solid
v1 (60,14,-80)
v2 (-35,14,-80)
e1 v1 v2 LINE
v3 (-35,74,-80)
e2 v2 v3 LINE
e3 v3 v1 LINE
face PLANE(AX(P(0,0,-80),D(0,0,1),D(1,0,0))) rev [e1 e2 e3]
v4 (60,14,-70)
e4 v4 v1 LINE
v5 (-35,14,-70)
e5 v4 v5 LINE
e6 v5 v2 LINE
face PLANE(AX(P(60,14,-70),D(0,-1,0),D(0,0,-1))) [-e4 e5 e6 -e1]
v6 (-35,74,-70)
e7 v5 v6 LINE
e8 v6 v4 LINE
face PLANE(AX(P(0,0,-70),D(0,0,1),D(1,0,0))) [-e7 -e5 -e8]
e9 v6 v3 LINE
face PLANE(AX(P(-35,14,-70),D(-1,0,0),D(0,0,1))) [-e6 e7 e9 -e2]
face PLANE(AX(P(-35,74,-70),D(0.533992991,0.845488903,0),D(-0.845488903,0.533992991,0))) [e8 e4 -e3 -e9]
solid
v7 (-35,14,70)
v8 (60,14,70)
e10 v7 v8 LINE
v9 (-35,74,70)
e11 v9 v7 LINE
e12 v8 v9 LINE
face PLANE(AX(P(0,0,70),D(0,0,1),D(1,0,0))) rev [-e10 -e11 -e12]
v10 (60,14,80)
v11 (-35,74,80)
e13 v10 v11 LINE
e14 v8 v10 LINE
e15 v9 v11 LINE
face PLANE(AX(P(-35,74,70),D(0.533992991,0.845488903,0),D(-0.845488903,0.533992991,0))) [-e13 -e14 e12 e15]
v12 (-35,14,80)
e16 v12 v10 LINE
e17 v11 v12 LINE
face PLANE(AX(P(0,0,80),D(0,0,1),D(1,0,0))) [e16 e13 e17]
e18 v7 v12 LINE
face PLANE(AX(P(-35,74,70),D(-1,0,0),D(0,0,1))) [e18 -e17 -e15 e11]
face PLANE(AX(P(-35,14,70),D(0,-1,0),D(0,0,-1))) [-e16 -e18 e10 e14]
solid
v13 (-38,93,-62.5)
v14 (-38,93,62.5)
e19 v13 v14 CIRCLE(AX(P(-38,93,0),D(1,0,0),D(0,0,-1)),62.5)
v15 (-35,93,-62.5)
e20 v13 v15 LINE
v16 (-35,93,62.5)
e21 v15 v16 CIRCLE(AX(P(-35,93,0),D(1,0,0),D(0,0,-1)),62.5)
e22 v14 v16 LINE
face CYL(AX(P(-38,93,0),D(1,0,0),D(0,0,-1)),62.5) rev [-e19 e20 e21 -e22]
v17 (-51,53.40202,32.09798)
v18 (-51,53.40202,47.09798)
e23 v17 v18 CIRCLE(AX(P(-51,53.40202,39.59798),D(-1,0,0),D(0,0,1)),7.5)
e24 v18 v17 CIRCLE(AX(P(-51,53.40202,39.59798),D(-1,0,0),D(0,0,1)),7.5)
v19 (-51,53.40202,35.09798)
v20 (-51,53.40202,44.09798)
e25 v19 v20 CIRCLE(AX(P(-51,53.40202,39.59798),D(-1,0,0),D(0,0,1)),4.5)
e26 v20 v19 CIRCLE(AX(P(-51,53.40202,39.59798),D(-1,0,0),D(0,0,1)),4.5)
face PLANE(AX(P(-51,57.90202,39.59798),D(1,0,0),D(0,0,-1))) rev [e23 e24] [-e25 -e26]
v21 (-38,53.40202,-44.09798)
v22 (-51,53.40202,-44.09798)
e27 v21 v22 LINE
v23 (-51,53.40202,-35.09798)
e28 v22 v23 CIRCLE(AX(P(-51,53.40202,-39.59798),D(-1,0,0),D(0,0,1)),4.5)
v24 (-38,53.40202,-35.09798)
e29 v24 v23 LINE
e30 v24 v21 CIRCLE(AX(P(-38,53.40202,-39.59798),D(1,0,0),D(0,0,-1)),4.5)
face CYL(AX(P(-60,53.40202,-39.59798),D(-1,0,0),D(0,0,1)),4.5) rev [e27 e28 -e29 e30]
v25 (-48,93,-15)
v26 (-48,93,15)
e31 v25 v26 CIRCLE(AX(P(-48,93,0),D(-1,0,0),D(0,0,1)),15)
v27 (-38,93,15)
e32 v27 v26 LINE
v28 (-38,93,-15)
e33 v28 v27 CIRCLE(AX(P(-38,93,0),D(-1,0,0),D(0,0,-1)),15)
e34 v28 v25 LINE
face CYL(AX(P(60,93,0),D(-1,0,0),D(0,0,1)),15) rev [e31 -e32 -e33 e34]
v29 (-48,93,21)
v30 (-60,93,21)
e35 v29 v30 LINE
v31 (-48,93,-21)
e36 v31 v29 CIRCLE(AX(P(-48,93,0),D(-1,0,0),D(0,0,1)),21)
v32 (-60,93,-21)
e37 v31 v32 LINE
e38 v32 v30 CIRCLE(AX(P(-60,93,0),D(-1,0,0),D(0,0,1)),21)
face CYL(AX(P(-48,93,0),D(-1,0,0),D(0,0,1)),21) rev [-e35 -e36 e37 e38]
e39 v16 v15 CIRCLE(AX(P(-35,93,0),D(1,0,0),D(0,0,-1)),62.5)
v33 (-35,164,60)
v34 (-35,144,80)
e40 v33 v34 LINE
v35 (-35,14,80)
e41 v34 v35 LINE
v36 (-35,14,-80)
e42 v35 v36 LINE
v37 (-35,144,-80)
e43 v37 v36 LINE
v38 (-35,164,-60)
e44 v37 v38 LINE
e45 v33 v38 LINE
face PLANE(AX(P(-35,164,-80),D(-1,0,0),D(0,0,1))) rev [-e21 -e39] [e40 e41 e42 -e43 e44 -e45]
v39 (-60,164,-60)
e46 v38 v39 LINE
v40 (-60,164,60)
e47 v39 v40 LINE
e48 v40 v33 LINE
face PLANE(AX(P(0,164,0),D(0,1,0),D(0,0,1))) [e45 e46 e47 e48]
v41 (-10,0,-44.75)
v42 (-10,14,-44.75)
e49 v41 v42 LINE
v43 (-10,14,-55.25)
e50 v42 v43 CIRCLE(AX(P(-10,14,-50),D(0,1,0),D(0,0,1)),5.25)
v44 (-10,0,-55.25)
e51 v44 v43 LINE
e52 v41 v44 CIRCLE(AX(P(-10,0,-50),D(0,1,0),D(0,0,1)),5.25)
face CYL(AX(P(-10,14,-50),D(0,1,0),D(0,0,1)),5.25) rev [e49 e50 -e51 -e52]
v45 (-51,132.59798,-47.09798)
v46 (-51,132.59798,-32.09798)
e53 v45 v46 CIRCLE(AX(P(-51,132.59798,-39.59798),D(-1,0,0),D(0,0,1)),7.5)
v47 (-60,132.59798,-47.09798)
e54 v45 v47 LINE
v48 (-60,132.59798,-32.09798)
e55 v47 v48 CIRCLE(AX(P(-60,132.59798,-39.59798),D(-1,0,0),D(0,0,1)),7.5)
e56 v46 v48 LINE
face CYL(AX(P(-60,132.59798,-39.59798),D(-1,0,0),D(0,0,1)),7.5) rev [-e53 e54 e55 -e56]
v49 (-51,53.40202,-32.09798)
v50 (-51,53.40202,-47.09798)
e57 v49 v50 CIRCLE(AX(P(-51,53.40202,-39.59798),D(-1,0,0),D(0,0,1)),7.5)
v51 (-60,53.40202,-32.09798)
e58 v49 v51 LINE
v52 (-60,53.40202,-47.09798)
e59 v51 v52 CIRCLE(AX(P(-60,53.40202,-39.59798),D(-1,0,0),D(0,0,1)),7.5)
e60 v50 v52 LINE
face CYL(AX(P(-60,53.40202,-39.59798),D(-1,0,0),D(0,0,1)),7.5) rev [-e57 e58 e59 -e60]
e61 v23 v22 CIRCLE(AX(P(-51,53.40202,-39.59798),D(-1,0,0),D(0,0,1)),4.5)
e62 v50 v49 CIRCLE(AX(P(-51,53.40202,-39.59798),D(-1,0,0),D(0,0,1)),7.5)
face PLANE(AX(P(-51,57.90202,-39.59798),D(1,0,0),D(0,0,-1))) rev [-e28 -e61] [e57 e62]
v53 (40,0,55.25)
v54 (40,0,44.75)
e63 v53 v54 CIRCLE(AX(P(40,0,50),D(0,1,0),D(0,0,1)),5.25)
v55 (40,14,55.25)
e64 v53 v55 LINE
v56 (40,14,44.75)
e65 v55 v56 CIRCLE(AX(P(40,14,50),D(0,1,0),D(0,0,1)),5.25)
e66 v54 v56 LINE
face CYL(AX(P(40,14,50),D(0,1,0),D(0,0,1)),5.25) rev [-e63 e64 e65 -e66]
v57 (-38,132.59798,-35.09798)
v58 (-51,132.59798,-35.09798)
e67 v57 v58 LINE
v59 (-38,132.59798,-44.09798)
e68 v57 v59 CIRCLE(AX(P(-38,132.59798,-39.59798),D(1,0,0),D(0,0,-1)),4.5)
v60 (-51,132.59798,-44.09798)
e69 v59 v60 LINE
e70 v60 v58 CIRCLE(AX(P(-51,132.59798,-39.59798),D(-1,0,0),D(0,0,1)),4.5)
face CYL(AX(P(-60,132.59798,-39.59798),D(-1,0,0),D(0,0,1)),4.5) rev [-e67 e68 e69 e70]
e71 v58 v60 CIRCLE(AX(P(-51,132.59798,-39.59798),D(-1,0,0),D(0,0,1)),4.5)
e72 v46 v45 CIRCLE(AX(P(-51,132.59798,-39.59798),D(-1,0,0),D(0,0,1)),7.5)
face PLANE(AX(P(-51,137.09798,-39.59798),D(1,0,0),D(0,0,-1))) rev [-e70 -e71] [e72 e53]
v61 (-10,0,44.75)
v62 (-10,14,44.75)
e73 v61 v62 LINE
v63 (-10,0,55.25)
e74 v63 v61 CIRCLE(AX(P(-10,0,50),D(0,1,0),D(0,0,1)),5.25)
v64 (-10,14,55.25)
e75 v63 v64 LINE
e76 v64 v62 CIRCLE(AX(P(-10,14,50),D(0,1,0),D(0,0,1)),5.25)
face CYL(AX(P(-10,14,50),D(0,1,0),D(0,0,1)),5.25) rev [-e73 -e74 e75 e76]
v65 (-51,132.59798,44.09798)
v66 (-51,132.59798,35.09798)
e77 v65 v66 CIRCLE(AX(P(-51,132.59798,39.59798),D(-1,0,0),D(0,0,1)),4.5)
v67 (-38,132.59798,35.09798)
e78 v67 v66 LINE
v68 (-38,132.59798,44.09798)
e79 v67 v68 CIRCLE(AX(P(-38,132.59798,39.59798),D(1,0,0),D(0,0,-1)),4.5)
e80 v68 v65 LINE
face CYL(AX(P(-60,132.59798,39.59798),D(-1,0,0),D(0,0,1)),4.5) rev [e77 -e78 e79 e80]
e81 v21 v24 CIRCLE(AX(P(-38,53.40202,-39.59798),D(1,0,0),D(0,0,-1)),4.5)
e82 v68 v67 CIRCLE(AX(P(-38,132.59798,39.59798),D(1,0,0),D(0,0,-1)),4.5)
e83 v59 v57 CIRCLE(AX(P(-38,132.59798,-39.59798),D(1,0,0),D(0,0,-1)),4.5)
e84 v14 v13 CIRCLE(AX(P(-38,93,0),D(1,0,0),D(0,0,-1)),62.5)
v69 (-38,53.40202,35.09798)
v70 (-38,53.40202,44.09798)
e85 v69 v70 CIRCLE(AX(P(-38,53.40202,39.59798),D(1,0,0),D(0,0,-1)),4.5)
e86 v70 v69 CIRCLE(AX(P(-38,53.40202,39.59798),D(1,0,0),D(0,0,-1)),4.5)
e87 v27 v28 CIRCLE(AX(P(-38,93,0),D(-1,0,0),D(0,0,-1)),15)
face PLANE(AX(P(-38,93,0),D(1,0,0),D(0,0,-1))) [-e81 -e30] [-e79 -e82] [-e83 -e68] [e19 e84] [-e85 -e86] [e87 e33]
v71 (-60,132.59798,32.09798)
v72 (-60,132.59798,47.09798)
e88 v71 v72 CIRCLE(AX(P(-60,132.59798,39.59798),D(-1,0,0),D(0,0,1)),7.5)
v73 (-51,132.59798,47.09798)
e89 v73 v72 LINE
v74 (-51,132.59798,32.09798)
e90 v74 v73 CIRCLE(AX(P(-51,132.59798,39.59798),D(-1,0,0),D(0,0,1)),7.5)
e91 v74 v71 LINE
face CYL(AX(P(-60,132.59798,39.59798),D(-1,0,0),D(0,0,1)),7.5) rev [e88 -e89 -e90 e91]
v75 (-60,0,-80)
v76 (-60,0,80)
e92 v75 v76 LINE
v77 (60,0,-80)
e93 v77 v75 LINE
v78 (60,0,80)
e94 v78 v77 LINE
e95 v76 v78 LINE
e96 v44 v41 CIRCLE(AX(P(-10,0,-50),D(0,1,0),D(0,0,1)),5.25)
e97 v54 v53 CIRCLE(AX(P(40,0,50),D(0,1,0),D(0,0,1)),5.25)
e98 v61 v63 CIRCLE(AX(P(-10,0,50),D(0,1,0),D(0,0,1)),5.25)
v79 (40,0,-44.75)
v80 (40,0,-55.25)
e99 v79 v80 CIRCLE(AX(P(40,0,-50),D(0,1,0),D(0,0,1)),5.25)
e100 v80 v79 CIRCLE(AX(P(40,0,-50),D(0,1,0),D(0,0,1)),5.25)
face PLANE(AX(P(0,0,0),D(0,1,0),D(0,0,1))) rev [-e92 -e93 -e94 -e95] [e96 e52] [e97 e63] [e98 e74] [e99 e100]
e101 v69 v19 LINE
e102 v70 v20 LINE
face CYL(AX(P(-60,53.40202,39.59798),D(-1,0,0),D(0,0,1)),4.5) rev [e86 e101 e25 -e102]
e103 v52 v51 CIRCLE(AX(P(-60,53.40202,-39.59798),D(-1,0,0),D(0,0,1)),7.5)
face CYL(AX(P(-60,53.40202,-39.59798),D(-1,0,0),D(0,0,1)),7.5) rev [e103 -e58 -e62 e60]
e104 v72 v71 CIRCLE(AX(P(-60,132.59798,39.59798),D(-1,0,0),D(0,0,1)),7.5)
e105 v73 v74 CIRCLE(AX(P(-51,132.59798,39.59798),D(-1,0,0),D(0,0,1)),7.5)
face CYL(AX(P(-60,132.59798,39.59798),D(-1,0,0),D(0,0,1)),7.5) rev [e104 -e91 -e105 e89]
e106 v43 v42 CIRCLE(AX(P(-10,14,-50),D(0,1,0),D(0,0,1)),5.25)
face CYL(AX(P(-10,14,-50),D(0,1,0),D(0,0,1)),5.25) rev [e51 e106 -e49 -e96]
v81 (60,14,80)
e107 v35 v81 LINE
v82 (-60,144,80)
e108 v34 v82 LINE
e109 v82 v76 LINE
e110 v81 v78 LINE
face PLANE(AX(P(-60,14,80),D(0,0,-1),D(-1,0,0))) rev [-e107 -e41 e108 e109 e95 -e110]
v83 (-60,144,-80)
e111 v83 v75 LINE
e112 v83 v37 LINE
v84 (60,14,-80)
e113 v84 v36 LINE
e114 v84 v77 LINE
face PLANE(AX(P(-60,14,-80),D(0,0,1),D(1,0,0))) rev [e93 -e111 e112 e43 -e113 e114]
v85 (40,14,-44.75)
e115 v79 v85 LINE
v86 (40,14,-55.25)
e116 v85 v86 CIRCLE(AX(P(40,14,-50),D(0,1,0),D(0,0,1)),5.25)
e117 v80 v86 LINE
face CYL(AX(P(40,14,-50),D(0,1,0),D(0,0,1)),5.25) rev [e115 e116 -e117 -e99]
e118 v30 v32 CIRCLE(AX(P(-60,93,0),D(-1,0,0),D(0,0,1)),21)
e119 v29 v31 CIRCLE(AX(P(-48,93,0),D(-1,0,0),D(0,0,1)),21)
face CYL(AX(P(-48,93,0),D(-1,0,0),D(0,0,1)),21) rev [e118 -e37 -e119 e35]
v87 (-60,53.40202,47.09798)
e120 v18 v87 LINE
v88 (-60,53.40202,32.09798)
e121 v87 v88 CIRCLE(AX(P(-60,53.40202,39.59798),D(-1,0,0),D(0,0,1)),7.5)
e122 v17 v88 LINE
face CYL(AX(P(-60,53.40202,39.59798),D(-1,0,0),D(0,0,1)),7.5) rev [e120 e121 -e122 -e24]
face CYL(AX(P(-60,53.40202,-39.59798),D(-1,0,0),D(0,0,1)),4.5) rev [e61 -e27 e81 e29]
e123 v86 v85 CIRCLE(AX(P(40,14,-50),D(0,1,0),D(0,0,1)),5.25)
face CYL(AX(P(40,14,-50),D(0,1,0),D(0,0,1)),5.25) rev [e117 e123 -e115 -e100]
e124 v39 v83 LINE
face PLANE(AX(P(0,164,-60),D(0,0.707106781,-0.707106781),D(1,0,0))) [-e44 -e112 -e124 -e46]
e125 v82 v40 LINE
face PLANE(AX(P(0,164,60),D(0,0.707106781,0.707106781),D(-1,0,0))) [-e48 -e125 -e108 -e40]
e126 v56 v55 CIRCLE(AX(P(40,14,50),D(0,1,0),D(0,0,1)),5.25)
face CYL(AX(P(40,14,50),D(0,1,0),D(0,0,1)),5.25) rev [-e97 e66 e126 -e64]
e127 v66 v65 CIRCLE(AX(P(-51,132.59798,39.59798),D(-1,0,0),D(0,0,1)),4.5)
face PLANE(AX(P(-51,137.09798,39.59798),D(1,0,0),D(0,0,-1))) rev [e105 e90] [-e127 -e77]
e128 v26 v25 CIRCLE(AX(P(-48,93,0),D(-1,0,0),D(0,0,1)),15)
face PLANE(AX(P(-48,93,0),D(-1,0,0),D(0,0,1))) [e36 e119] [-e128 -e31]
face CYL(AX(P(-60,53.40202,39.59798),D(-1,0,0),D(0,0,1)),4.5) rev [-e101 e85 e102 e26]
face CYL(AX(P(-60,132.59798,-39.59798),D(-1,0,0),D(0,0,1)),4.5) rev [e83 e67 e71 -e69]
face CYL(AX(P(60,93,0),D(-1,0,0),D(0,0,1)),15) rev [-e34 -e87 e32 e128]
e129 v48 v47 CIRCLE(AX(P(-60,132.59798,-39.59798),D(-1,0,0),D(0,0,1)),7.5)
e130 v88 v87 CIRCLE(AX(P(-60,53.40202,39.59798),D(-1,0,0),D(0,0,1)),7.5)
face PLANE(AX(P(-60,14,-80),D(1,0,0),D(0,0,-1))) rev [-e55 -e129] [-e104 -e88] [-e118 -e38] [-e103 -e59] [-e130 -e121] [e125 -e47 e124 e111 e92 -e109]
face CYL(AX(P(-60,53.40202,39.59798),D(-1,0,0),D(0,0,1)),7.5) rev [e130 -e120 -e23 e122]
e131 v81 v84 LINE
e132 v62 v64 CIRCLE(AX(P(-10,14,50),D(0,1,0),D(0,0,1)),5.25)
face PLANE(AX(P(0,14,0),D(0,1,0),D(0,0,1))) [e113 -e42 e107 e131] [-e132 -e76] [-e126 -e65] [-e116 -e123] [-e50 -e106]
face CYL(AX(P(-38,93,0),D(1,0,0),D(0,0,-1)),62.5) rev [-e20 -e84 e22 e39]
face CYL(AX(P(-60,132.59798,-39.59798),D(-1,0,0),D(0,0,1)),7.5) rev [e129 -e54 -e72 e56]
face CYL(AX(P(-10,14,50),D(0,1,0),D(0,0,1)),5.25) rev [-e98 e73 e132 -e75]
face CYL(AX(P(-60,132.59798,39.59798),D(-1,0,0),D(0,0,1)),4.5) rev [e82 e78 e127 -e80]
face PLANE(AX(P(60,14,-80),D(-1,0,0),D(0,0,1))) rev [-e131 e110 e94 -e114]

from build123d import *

# Parameters (mm, degrees)
SKETCH_1_W                         = 120
SKETCH_1_H                         = 160
EXTRUDE_1_DEPTH                    = 14
SKETCH_2_W                         = 25
SKETCH_2_H                         = 160
EXTRUDE_2_DEPTH                    = 150
EXTRUDE_3_DEPTH                    = 10
EXTRUDE_4_DEPTH                    = 10
SKETCH_5_R                         = 21
CUT_EXTRUDE_1_DEPTH                = 12
SKETCH_6_R                         = 15
CUT_EXTRUDE_2_DEPTH                = 213.037732491
SKETCH_7_R                         = 62.5
CUT_EXTRUDE_3_DEPTH                = 3
HOLE_WIZARD_10_5_10_5_1_AT_2_COUNT = 2
HOLE_WIZARD_10_5_10_5_1_AT_2_PITCH = 100
PATTERN_LINEAR_1_COUNT             = 2
PATTERN_LINEAR_1_PITCH             = 50
CHAMFER_1_SIZE                     = 20
PATTERN_CIRCULAR_1_COUNT           = 4


with BuildPart() as part:
    # 草图1 → 凸台-拉伸1 (new body)
    with BuildSketch(Plane(origin=(0, 0, 0), x_dir=(1, 0, 0), z_dir=(0, 1, 0))):
        Rectangle(SKETCH_1_W, SKETCH_1_H)
    extrude(amount=EXTRUDE_1_DEPTH)

    # 草图2 → 凸台-拉伸2 (add)
    with BuildSketch(Plane(origin=(0, 14, 0), x_dir=(1, 0, 0), z_dir=(0, 1, 0))):
        with Locations((-47.5, 0)):
            Rectangle(SKETCH_2_W, SKETCH_2_H)
    extrude(amount=EXTRUDE_2_DEPTH)

    # 草图5 → 切除-拉伸1 (cut)
    with BuildSketch(Plane.ZY.offset(60)):
        with Locations((0, 93)):
            Circle(SKETCH_5_R)
    extrude(amount=-CUT_EXTRUDE_1_DEPTH, mode=Mode.SUBTRACT)

    # 草图6 → 切除-拉伸2 (cut, through all)
    with BuildSketch(Plane.ZY.offset(48)):
        with Locations((0, 93)):
            Circle(SKETCH_6_R)
    extrude(amount=-CUT_EXTRUDE_2_DEPTH, mode=Mode.SUBTRACT)

    # 草图7 → 切除-拉伸3 (cut)
    with BuildSketch(Plane(origin=(-35, 0, 0), x_dir=(0, 0, -1), z_dir=(1, 0, 0))):
        with Locations((0, 93)):
            Circle(SKETCH_7_R)
    extrude(amount=-CUT_EXTRUDE_3_DEPTH, mode=Mode.SUBTRACT)

    # 草图9 → Ø10.5 (10.5) 直径孔1 (revolve, cut)
    with BuildSketch(Plane(origin=(40, 14, -50), x_dir=(0, 0, 1), z_dir=(1, 0, 0))):
        Polygon((0, 0), (0, 18.15451825), (5.25, 15), (5.25, 0), align=None)
    hole_wizard_10_5_10_5_1 = revolve(axis=Axis((40, 20.35, -50), (0, -1, 0)), mode=Mode.SUBTRACT)

    # Ø10.5 (10.5) 直径孔1 at 2: Ø10.5 (10.5) 直径孔1 ×2
    with Locations(*[(0, 0, i * HOLE_WIZARD_10_5_10_5_1_AT_2_PITCH) for i in range(1, HOLE_WIZARD_10_5_10_5_1_AT_2_COUNT)]):
        add(hole_wizard_10_5_10_5_1, mode=Mode.SUBTRACT)

    # 阵列(线性)1: Ø10.5 (10.5) 直径孔1 ×2
    with Locations(*[(-i * PATTERN_LINEAR_1_PITCH, 0, 0) for i in range(1, PATTERN_LINEAR_1_COUNT)]):
        add(hole_wizard_10_5_10_5_1, mode=Mode.SUBTRACT)

    # 阵列(线性)1 copy 1 sketch → 阵列(线性)1 copy 1 (revolve, cut)
    with BuildSketch(Plane(origin=(-10, 14, 50), x_dir=(0, 0, 1), z_dir=(1, 0, 0))):
        Polygon((0, 0), (0, 18.15451825), (5.25, 15), (5.25, 0), align=None)
    revolve(axis=Axis((-10, 20.35, 50), (0, -1, 0)), mode=Mode.SUBTRACT)

    # 倒角1
    chamfer_1_edges = [part.edges().sort_by_distance(p)[0] for p in [
        (-47.5, 164, 80),
        (-47.5, 164, -80),
    ]]
    chamfer(chamfer_1_edges, length=CHAMFER_1_SIZE)

    # 草图11 → 打孔尺寸(%根据)内六角圆柱头螺钉的类型1 (revolve, cut)
    with BuildSketch(Plane(origin=(-60, 132.597979746, -39.597979746), x_dir=(0, 0, 1), z_dir=(0, 1, 0))):
        Polygon((0, 0), (0, 120), (4.5, 120), (4.5, 9), (7.5, 9), (7.5, 0), align=None)
    hole_wizard_1 = revolve(axis=Axis((-66.35, 132.597979746, -39.597979746), (1, 0, 0)), mode=Mode.SUBTRACT)

    # 阵列(圆周)1: 打孔尺寸(%根据)内六角圆柱头螺钉的类型1 ×4 about axis
    pattern_circular_1_axis = Axis((0, 93, 0), (1, 0, 0))
    for i in range(1, PATTERN_CIRCULAR_1_COUNT):
        add(hole_wizard_1.rotate(pattern_circular_1_axis, i * 360 / PATTERN_CIRCULAR_1_COUNT), mode=Mode.SUBTRACT)


with BuildPart() as body_2:
    # 草图3 → 凸台-拉伸3 (new body)
    with BuildSketch(Plane.XY.offset(80)):
        Polygon((-35, 74), (60, 14), (-35, 14), align=None)
    extrude(amount=-EXTRUDE_3_DEPTH)


with BuildPart() as body_3:
    # 草图4 → 凸台-拉伸4 (new body)
    with BuildSketch(Plane(origin=(0, 0, -80), x_dir=(-1, 0, 0), z_dir=(0, 0, -1))):
        Polygon((35, 14), (35, 74), (-60, 14), align=None)
    extrude(amount=-EXTRUDE_4_DEPTH)


solid = Compound([part.part, body_2.part, body_3.part])
